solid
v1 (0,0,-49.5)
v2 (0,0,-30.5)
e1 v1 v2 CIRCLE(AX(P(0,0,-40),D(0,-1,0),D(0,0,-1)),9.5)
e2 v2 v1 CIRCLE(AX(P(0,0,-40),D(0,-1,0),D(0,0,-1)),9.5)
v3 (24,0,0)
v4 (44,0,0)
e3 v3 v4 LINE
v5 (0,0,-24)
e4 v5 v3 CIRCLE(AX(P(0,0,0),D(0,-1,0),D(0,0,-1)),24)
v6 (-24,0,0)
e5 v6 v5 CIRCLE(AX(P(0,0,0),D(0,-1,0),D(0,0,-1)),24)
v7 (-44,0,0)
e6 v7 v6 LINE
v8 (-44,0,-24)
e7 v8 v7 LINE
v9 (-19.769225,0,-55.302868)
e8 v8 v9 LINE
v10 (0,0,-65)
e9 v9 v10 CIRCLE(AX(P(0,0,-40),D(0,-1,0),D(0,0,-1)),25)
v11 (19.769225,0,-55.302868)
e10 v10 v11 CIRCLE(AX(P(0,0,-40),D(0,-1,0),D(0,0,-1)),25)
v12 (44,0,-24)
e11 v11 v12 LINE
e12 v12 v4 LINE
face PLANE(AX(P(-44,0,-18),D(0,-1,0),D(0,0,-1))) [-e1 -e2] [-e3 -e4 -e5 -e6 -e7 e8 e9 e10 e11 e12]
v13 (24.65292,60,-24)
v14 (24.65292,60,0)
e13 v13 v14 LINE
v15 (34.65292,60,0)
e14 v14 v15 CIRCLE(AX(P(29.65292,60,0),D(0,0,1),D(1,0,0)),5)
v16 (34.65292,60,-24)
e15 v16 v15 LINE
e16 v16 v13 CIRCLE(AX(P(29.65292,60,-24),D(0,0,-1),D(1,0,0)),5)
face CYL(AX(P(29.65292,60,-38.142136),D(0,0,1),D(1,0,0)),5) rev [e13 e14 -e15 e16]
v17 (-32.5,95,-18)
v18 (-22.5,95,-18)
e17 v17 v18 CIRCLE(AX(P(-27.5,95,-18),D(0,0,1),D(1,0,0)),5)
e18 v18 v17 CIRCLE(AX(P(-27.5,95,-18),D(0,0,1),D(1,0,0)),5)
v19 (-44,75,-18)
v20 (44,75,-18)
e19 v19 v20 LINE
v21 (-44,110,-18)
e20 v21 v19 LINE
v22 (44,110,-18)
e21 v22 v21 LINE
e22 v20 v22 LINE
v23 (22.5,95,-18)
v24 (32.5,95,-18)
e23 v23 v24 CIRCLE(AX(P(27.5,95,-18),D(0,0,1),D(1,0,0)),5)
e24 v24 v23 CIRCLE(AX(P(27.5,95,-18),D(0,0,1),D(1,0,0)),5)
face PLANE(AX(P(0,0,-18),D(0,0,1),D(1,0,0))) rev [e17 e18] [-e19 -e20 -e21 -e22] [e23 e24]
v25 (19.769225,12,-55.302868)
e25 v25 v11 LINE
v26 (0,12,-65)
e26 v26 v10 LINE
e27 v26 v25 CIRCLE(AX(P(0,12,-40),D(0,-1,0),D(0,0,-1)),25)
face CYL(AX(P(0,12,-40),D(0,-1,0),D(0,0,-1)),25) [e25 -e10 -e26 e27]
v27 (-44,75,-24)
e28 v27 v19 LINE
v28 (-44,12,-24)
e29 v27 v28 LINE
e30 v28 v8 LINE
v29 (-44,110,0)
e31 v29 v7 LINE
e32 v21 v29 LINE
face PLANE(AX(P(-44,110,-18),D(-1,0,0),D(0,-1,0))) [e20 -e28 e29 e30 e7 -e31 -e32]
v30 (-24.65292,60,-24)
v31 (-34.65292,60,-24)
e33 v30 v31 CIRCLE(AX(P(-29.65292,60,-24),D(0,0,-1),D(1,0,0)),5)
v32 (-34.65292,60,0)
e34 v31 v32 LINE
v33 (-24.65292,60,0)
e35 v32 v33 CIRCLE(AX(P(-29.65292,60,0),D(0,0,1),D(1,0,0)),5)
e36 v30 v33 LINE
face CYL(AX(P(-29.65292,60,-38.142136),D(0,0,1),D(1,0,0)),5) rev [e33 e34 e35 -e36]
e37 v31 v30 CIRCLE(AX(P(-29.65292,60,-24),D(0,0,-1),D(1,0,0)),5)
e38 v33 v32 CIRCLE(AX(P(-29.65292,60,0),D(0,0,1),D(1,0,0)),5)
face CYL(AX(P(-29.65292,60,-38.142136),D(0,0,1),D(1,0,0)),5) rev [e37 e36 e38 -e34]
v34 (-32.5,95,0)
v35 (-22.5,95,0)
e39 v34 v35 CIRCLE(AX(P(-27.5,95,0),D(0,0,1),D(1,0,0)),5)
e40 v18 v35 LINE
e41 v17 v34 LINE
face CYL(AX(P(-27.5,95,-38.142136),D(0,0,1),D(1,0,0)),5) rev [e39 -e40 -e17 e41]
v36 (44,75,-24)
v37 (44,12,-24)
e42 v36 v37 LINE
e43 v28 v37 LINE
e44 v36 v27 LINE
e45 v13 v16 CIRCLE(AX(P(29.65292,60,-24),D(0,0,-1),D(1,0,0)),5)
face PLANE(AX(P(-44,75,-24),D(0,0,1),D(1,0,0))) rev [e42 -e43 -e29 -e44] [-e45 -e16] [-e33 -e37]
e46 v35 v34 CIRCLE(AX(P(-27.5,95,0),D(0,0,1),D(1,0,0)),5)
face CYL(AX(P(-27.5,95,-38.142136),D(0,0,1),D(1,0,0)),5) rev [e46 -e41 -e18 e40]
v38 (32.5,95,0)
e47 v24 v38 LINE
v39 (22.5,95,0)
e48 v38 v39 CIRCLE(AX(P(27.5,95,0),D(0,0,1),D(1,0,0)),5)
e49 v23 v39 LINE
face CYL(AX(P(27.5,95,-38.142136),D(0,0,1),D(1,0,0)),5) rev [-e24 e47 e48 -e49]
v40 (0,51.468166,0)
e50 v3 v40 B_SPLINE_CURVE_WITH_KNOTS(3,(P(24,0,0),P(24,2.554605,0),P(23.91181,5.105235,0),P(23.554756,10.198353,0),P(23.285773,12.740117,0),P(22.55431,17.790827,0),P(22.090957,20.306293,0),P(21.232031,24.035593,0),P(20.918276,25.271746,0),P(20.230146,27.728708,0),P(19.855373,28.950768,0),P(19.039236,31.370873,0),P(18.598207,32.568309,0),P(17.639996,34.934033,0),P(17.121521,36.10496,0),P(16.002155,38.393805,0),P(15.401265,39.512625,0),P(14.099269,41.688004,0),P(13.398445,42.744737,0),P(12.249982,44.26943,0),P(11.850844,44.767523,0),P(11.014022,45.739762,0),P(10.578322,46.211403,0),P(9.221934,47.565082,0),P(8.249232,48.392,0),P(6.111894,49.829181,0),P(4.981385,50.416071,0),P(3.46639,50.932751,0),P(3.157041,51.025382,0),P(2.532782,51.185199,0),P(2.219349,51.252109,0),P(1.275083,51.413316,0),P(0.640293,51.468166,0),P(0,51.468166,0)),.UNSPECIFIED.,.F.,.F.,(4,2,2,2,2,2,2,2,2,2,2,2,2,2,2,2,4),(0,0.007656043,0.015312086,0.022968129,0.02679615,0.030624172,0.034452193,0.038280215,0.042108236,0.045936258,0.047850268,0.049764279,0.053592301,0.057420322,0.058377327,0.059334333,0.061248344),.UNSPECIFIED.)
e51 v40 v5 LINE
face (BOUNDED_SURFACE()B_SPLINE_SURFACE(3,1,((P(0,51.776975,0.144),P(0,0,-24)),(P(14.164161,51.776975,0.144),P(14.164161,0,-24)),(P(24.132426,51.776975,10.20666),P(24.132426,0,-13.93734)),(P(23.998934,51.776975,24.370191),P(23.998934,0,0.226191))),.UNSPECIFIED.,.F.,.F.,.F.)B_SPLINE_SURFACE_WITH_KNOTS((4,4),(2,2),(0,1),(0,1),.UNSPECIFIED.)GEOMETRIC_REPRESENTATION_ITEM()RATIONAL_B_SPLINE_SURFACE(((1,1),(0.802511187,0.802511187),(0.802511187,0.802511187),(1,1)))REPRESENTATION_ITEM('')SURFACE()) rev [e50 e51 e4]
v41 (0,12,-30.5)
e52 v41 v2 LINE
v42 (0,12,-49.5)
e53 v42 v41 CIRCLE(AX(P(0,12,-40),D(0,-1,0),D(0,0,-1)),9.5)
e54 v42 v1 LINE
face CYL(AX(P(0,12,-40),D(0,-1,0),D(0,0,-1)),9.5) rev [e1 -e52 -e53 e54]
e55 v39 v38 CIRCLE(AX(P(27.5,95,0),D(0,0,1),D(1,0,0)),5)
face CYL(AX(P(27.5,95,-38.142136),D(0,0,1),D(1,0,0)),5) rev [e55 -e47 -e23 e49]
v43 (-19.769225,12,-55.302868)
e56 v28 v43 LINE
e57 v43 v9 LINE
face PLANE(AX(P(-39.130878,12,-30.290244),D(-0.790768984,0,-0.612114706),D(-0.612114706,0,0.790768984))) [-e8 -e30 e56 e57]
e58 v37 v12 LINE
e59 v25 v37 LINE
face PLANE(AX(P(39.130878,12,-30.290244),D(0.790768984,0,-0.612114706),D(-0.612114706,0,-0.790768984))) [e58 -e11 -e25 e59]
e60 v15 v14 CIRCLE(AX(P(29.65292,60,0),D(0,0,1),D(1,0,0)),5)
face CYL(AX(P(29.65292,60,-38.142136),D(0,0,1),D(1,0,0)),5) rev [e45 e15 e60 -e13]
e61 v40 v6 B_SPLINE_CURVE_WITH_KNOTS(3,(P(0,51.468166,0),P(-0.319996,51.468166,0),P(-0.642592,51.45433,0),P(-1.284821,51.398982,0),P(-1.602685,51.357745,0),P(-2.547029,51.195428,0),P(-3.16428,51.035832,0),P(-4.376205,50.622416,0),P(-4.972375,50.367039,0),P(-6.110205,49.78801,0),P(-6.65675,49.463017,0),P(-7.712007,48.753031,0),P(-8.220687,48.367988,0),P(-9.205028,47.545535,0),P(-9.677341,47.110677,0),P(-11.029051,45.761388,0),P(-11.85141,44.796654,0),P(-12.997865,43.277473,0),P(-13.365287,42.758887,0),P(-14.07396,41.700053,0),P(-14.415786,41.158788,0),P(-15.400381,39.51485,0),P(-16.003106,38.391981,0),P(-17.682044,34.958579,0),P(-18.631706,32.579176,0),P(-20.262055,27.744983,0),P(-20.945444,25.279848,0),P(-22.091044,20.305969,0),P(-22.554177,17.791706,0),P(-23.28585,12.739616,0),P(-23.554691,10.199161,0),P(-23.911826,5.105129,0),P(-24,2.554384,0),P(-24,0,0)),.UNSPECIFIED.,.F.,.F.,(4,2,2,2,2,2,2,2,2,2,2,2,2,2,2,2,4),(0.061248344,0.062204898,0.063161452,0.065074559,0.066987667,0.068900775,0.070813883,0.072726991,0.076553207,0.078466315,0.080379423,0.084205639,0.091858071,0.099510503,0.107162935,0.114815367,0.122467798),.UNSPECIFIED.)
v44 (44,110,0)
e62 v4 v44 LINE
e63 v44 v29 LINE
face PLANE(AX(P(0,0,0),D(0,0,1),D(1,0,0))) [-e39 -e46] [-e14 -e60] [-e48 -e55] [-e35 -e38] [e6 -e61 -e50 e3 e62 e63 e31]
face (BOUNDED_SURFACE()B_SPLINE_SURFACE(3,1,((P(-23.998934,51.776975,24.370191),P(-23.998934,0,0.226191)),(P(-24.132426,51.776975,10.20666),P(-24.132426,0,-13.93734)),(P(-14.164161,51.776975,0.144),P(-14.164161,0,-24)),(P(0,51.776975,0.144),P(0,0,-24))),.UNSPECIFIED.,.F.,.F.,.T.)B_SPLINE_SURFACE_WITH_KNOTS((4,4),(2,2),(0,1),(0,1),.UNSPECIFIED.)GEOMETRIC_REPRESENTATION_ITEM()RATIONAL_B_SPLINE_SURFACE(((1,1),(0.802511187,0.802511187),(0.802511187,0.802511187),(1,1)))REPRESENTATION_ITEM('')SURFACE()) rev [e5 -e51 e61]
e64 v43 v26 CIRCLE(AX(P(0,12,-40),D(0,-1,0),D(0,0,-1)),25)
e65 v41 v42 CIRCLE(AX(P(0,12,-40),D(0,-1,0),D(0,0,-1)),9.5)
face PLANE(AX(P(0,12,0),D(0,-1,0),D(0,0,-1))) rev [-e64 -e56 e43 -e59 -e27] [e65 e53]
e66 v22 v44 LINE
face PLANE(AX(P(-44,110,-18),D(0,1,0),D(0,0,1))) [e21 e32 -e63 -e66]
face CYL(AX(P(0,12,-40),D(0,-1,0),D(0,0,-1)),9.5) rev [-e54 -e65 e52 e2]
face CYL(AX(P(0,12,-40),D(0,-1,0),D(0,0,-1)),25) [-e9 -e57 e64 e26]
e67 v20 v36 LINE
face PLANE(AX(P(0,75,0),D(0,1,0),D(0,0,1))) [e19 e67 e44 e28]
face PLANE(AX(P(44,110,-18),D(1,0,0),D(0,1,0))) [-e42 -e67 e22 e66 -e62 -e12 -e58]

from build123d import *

# Parameters (mm, degrees)
BASE_PLATE_SKETCH_W = 88
BASE_PLATE_SKETCH_H = 110
BASE_PLATE_DEPTH    = 18
SIDE_BOSS_SKETCH_W  = 88
SIDE_BOSS_SKETCH_H  = 6
SIDE_BOSS_DEPTH     = 75
REAR_BOSS_SKETCH_R  = 9.5
REAR_BOSS_DEPTH     = 12
ANGLED_CUT_REACH    = 137.133
ANGLED_CUT_SKETCH_R = 5
ARCH_CUT_SKETCH_R   = 24
ARCH_CUT_DEPTH      = 93.743251702


with BuildPart() as part:
    # Base Plate Sketch → Base Plate (new body)
    with BuildSketch(Plane.XY):
        with Locations((0, 55)):
            Rectangle(BASE_PLATE_SKETCH_W, BASE_PLATE_SKETCH_H)
    extrude(amount=-BASE_PLATE_DEPTH)

    # Side Boss Sketch → Side Boss (add)
    with BuildSketch(Plane(origin=(0, 0, 0), x_dir=(1, 0, 0), z_dir=(0, 1, 0))):
        with Locations((0, 21)):
            Rectangle(SIDE_BOSS_SKETCH_W, SIDE_BOSS_SKETCH_H)
    extrude(amount=SIDE_BOSS_DEPTH)

    # Rear Boss Sketch → Rear Boss (add)
    with BuildSketch(Plane.XZ):
        with BuildLine():
            Line((-44, -24), (-19.769224603, -55.302867659))
            ThreePointArc((-19.769224603, -55.302867659), (0, -65), (19.769224603, -55.302867659))
            Line((19.769224603, -55.302867659), (44, -24))
            Line((44, -24), (-44, -24))
        make_face()
        with Locations(Location((0, -40, 0), (0, 0, 270))):
            Circle(REAR_BOSS_SKETCH_R, mode=Mode.SUBTRACT)
    extrude(amount=-REAR_BOSS_DEPTH)

    # Angled Cut: up to this face of the body (flat: up to its plane)
    angled_cut_end = Plane(part.part.faces().sort_by_distance((0, 43.5, -24))[0])
    # Angled Cut Sketch → Angled Cut (cut, up to the picked face)
    with BuildSketch(Plane.XY, mode=Mode.PRIVATE) as angled_cut_sk1:
        with Locations((-27.5, 95)):
            Circle(ANGLED_CUT_SKETCH_R)
    angled_cut_tool1 = split(extrude(angled_cut_sk1.sketch, amount=-ANGLED_CUT_REACH, mode=Mode.PRIVATE), bisect_by=angled_cut_end, keep=Keep.BOTH, mode=Mode.PRIVATE)
    # Angled Cut Sketch → Angled Cut (cut, up to the picked face)
    with BuildSketch(Plane.XY, mode=Mode.PRIVATE) as angled_cut_sk2:
        with Locations((27.5, 95)):
            Circle(ANGLED_CUT_SKETCH_R)
    angled_cut_tool2 = split(extrude(angled_cut_sk2.sketch, amount=-ANGLED_CUT_REACH, mode=Mode.PRIVATE), bisect_by=angled_cut_end, keep=Keep.BOTH, mode=Mode.PRIVATE)
    # Angled Cut Sketch → Angled Cut (cut, up to the picked face)
    with BuildSketch(Plane.XY, mode=Mode.PRIVATE) as angled_cut_sk3:
        with Locations((29.652920455, 60)):
            Circle(ANGLED_CUT_SKETCH_R)
    angled_cut_tool3 = split(extrude(angled_cut_sk3.sketch, amount=-ANGLED_CUT_REACH, mode=Mode.PRIVATE), bisect_by=angled_cut_end, keep=Keep.BOTH, mode=Mode.PRIVATE)
    # Angled Cut Sketch → Angled Cut (cut, up to the picked face)
    with BuildSketch(Plane.XY, mode=Mode.PRIVATE) as angled_cut_sk4:
        with Locations((-29.652920455, 60)):
            Circle(ANGLED_CUT_SKETCH_R)
    angled_cut_tool4 = split(extrude(angled_cut_sk4.sketch, amount=-ANGLED_CUT_REACH, mode=Mode.PRIVATE), bisect_by=angled_cut_end, keep=Keep.BOTH, mode=Mode.PRIVATE)
    add(angled_cut_tool1.solids().sort_by(Axis((-27.5, 95, 0), (0, 0, -1)))[0], mode=Mode.SUBTRACT)
    add(angled_cut_tool2.solids().sort_by(Axis((27.5, 95, 0), (0, 0, -1)))[0], mode=Mode.SUBTRACT)
    add(angled_cut_tool3.solids().sort_by(Axis((29.65292, 60, 0), (0, 0, -1)))[0], mode=Mode.SUBTRACT)
    add(angled_cut_tool4.solids().sort_by(Axis((-29.65292, 60, 0), (0, 0, -1)))[0], mode=Mode.SUBTRACT)

    # Arch Cut Sketch → Arch Cut (cut, along a direction that is not the sketch's normal)
    with BuildSketch(Plane.XZ):
        Circle(ARCH_CUT_SKETCH_R)
    extrude(amount=-ARCH_CUT_DEPTH, dir=(0, -0.9063077870366493, -0.4226182617407009), mode=Mode.SUBTRACT)


solid = part.part
